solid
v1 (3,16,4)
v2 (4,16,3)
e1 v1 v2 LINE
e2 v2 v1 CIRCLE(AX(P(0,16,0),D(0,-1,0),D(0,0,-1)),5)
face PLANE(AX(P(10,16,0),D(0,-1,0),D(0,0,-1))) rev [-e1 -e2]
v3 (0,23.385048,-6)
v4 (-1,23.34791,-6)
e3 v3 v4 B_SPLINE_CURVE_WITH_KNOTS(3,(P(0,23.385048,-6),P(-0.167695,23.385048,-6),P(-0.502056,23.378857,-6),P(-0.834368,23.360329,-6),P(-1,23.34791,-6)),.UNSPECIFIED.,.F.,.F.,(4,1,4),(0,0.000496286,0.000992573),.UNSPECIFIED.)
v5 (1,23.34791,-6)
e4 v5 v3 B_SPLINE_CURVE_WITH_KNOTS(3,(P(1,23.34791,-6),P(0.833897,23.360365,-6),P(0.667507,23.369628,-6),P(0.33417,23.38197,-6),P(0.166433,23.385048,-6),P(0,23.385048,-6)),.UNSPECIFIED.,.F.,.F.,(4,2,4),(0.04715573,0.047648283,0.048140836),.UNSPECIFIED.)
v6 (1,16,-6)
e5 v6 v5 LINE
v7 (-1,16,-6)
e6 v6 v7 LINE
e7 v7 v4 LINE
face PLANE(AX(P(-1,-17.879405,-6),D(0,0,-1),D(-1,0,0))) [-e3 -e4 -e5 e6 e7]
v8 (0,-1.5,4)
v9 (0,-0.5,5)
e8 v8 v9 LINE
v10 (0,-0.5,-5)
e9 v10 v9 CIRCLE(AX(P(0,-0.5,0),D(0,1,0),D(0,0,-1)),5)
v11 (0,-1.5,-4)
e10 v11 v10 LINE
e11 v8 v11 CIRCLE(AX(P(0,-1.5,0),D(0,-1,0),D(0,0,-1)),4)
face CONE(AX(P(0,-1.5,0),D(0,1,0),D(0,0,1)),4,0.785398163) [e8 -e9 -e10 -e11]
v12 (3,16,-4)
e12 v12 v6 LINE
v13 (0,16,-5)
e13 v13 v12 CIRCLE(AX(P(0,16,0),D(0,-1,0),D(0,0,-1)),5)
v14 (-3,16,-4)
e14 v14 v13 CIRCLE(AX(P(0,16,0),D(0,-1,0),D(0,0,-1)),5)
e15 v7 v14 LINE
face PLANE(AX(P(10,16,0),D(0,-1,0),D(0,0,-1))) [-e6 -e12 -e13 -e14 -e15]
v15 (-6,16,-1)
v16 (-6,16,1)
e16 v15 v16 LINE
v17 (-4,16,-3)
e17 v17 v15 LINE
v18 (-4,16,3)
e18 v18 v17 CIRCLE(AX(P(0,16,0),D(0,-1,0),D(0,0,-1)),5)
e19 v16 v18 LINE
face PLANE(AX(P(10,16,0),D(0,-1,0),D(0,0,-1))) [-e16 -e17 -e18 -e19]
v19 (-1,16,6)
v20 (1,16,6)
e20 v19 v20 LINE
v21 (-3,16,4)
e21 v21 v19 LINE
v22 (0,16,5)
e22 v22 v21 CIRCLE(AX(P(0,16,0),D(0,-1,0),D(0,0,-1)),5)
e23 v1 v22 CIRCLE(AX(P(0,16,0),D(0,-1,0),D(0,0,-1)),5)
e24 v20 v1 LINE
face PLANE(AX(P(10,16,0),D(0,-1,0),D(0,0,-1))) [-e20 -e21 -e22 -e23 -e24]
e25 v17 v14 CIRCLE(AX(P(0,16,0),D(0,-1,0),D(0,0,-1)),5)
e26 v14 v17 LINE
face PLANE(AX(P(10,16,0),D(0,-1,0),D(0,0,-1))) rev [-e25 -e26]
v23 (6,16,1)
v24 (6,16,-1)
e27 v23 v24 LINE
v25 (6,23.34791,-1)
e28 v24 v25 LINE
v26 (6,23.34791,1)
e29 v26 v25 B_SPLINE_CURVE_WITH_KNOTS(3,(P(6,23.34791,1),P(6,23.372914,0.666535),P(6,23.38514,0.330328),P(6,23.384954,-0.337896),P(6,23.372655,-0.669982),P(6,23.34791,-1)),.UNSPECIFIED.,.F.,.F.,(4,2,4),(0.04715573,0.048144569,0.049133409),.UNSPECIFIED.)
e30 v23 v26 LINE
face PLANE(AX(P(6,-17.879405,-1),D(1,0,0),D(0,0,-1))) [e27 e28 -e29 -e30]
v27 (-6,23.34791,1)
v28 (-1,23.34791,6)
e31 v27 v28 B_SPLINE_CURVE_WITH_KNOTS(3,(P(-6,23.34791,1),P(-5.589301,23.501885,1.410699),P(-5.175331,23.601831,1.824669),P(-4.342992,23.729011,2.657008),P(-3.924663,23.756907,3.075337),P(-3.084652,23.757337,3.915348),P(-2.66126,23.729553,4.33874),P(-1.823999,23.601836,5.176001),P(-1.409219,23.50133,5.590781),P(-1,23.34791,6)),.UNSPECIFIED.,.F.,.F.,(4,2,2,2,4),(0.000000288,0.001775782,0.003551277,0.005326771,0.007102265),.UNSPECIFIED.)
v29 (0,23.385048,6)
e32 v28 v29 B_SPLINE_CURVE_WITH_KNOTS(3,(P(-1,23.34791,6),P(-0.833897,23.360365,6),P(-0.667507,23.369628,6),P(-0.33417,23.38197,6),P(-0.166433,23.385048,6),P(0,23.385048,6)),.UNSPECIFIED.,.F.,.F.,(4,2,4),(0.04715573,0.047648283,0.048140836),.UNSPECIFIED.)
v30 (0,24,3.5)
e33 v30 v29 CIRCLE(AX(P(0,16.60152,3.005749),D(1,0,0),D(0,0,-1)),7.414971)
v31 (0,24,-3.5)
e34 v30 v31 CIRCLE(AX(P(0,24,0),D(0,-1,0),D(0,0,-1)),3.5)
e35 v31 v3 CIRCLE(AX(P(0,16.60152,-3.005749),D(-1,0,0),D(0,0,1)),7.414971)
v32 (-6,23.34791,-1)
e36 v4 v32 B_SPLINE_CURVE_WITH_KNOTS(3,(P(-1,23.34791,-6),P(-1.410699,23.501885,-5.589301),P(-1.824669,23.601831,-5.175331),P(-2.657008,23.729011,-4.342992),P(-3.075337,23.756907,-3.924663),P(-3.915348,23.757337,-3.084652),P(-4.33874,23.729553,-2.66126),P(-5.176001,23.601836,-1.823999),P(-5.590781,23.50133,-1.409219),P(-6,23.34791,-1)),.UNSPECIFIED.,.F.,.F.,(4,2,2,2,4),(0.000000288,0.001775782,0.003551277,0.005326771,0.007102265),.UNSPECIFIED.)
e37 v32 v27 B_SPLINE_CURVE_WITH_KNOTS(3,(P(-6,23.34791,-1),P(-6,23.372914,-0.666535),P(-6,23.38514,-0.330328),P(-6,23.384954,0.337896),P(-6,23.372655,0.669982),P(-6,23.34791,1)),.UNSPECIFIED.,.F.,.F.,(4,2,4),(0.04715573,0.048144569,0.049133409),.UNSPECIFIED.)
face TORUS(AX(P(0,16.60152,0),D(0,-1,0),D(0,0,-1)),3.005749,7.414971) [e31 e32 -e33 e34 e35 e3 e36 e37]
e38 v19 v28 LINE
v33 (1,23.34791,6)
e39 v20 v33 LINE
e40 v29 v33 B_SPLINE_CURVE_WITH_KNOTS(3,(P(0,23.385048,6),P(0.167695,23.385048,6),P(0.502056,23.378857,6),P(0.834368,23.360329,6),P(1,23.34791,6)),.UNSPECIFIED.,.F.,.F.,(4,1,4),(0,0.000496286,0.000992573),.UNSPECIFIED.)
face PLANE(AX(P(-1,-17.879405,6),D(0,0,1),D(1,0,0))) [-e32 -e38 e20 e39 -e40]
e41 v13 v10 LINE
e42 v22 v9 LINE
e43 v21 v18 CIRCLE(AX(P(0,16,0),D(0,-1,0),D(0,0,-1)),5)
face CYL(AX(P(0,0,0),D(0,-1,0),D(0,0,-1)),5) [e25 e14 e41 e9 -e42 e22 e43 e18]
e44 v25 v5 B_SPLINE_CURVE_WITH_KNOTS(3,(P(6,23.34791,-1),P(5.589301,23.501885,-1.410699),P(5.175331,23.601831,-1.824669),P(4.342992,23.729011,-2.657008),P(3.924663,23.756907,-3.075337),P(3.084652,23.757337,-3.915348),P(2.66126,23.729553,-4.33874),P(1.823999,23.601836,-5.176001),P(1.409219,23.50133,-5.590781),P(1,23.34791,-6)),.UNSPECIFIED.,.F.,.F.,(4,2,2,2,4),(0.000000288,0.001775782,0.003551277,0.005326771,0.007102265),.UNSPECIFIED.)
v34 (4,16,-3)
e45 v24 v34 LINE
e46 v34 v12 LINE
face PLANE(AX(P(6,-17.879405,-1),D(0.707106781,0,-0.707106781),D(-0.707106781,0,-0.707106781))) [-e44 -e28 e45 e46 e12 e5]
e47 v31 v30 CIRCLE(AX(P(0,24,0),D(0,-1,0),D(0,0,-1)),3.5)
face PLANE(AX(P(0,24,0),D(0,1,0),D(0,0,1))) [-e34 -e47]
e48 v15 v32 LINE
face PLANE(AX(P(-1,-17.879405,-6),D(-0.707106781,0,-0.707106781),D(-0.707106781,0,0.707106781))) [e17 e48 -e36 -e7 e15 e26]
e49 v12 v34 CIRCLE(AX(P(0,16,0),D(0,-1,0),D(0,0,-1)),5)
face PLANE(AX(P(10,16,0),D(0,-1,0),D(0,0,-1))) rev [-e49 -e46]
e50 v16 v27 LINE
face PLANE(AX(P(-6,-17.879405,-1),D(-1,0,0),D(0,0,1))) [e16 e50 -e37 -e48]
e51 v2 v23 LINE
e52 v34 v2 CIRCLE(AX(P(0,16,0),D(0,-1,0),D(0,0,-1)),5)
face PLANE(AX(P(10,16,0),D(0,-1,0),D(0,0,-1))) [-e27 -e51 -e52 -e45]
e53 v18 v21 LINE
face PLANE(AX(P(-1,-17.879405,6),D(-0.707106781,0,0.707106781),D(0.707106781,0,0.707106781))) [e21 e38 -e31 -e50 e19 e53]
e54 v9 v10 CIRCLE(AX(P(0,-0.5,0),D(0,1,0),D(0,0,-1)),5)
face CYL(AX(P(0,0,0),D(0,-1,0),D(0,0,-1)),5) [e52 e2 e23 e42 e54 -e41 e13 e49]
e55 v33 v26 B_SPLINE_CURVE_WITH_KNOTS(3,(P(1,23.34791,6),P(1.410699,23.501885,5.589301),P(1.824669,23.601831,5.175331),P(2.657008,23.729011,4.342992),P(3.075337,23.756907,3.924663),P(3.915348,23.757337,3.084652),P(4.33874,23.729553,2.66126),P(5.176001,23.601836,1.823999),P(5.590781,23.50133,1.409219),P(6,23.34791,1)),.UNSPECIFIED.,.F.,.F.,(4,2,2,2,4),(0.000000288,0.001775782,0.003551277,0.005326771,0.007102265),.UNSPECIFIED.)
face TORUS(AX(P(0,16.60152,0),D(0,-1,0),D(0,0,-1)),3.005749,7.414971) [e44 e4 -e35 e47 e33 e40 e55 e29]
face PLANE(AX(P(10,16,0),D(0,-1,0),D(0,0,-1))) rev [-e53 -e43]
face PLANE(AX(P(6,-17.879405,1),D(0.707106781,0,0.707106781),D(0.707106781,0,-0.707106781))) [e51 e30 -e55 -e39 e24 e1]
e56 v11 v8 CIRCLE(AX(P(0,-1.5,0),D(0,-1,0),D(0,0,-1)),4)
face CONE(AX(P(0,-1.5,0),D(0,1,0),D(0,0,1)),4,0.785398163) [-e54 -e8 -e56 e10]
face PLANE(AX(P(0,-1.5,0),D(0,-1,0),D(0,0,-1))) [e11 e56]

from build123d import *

# Parameters (mm, degrees)
CHAMFER1_SIZE       = 1
SKETCH2_R           = 11.978178672
CUT_EXTRUDE2_DEPTH  = 8
SKETCH4_R           = 5
BOSS_EXTRUDE1_DEPTH = 1.5
CHAMFER2_SIZE       = 1


with BuildPart() as part:
    # Sketch1 → Revolve1 (revolve)
    with BuildSketch(Plane.XY, mode=Mode.PRIVATE) as revolve1_sk:
        Polygon((0, 0), (0, 24), (10, 24), (10, 16), (5, 16), (5, 0), align=None)
    revolve(revolve1_sk.sketch.rotate(Axis((0, 0, 0), (0, 1, 0)), 90), axis=Axis((0, 0, 0), (0, 1, 0)))

    # Chamfer1
    chamfer1_edges = [part.edges().sort_by_distance(p)[0] for p in [
        (0, 0, 5),
    ]]
    chamfer(chamfer1_edges, length=CHAMFER1_SIZE)

    # Sketch2 → Cut-Extrude2 (cut)
    with BuildSketch(Plane(origin=(0, 24, 0), x_dir=(1, 0, 0), z_dir=(0, 1, 0))):
        Circle(SKETCH2_R)
        Polygon((-1, 6), (1, 6), (6, 1), (6, -1), (1, -6), (-1, -6), (-6, -1), (-6, 1), align=None, mode=Mode.SUBTRACT)
    extrude(amount=-CUT_EXTRUDE2_DEPTH, mode=Mode.SUBTRACT)

    # Sketch3 → Cut-Revolve1 (revolve, cut)
    with BuildSketch(Plane.XY, mode=Mode.PRIVATE) as cut_revolve1_sk:
        with BuildLine():
            Line((3.5, 24), (5.57579334, 25.302795294))
            Line((5.57579334, 25.302795294), (6.462708925, 23.688216178))
            Line((6.462708925, 23.688216178), (6.758347453, 22.996814774))
            ThreePointArc((6.758347453, 22.996814774), (5.187612361, 23.688216178), (3.5, 24))
        make_face()
    revolve(cut_revolve1_sk.sketch.rotate(Axis((0, 0, 0), (0, 1, 0)), 90), axis=Axis((0, 0, 0), (0, 1, 0)), mode=Mode.SUBTRACT)

    # Sketch4 → Boss-Extrude1 (add, symmetric)
    with BuildSketch(Plane.XZ):
        with Locations(Location((0, 0, 0), (0, 0, 270))):
            Circle(SKETCH4_R)
    extrude(amount=BOSS_EXTRUDE1_DEPTH, both=True)

    # Chamfer2
    chamfer2_edges = [part.edges().sort_by_distance(p)[0] for p in [
        (0, -1.5, 5),
    ]]
    chamfer(chamfer2_edges, length=CHAMFER2_SIZE)


solid = part.part
